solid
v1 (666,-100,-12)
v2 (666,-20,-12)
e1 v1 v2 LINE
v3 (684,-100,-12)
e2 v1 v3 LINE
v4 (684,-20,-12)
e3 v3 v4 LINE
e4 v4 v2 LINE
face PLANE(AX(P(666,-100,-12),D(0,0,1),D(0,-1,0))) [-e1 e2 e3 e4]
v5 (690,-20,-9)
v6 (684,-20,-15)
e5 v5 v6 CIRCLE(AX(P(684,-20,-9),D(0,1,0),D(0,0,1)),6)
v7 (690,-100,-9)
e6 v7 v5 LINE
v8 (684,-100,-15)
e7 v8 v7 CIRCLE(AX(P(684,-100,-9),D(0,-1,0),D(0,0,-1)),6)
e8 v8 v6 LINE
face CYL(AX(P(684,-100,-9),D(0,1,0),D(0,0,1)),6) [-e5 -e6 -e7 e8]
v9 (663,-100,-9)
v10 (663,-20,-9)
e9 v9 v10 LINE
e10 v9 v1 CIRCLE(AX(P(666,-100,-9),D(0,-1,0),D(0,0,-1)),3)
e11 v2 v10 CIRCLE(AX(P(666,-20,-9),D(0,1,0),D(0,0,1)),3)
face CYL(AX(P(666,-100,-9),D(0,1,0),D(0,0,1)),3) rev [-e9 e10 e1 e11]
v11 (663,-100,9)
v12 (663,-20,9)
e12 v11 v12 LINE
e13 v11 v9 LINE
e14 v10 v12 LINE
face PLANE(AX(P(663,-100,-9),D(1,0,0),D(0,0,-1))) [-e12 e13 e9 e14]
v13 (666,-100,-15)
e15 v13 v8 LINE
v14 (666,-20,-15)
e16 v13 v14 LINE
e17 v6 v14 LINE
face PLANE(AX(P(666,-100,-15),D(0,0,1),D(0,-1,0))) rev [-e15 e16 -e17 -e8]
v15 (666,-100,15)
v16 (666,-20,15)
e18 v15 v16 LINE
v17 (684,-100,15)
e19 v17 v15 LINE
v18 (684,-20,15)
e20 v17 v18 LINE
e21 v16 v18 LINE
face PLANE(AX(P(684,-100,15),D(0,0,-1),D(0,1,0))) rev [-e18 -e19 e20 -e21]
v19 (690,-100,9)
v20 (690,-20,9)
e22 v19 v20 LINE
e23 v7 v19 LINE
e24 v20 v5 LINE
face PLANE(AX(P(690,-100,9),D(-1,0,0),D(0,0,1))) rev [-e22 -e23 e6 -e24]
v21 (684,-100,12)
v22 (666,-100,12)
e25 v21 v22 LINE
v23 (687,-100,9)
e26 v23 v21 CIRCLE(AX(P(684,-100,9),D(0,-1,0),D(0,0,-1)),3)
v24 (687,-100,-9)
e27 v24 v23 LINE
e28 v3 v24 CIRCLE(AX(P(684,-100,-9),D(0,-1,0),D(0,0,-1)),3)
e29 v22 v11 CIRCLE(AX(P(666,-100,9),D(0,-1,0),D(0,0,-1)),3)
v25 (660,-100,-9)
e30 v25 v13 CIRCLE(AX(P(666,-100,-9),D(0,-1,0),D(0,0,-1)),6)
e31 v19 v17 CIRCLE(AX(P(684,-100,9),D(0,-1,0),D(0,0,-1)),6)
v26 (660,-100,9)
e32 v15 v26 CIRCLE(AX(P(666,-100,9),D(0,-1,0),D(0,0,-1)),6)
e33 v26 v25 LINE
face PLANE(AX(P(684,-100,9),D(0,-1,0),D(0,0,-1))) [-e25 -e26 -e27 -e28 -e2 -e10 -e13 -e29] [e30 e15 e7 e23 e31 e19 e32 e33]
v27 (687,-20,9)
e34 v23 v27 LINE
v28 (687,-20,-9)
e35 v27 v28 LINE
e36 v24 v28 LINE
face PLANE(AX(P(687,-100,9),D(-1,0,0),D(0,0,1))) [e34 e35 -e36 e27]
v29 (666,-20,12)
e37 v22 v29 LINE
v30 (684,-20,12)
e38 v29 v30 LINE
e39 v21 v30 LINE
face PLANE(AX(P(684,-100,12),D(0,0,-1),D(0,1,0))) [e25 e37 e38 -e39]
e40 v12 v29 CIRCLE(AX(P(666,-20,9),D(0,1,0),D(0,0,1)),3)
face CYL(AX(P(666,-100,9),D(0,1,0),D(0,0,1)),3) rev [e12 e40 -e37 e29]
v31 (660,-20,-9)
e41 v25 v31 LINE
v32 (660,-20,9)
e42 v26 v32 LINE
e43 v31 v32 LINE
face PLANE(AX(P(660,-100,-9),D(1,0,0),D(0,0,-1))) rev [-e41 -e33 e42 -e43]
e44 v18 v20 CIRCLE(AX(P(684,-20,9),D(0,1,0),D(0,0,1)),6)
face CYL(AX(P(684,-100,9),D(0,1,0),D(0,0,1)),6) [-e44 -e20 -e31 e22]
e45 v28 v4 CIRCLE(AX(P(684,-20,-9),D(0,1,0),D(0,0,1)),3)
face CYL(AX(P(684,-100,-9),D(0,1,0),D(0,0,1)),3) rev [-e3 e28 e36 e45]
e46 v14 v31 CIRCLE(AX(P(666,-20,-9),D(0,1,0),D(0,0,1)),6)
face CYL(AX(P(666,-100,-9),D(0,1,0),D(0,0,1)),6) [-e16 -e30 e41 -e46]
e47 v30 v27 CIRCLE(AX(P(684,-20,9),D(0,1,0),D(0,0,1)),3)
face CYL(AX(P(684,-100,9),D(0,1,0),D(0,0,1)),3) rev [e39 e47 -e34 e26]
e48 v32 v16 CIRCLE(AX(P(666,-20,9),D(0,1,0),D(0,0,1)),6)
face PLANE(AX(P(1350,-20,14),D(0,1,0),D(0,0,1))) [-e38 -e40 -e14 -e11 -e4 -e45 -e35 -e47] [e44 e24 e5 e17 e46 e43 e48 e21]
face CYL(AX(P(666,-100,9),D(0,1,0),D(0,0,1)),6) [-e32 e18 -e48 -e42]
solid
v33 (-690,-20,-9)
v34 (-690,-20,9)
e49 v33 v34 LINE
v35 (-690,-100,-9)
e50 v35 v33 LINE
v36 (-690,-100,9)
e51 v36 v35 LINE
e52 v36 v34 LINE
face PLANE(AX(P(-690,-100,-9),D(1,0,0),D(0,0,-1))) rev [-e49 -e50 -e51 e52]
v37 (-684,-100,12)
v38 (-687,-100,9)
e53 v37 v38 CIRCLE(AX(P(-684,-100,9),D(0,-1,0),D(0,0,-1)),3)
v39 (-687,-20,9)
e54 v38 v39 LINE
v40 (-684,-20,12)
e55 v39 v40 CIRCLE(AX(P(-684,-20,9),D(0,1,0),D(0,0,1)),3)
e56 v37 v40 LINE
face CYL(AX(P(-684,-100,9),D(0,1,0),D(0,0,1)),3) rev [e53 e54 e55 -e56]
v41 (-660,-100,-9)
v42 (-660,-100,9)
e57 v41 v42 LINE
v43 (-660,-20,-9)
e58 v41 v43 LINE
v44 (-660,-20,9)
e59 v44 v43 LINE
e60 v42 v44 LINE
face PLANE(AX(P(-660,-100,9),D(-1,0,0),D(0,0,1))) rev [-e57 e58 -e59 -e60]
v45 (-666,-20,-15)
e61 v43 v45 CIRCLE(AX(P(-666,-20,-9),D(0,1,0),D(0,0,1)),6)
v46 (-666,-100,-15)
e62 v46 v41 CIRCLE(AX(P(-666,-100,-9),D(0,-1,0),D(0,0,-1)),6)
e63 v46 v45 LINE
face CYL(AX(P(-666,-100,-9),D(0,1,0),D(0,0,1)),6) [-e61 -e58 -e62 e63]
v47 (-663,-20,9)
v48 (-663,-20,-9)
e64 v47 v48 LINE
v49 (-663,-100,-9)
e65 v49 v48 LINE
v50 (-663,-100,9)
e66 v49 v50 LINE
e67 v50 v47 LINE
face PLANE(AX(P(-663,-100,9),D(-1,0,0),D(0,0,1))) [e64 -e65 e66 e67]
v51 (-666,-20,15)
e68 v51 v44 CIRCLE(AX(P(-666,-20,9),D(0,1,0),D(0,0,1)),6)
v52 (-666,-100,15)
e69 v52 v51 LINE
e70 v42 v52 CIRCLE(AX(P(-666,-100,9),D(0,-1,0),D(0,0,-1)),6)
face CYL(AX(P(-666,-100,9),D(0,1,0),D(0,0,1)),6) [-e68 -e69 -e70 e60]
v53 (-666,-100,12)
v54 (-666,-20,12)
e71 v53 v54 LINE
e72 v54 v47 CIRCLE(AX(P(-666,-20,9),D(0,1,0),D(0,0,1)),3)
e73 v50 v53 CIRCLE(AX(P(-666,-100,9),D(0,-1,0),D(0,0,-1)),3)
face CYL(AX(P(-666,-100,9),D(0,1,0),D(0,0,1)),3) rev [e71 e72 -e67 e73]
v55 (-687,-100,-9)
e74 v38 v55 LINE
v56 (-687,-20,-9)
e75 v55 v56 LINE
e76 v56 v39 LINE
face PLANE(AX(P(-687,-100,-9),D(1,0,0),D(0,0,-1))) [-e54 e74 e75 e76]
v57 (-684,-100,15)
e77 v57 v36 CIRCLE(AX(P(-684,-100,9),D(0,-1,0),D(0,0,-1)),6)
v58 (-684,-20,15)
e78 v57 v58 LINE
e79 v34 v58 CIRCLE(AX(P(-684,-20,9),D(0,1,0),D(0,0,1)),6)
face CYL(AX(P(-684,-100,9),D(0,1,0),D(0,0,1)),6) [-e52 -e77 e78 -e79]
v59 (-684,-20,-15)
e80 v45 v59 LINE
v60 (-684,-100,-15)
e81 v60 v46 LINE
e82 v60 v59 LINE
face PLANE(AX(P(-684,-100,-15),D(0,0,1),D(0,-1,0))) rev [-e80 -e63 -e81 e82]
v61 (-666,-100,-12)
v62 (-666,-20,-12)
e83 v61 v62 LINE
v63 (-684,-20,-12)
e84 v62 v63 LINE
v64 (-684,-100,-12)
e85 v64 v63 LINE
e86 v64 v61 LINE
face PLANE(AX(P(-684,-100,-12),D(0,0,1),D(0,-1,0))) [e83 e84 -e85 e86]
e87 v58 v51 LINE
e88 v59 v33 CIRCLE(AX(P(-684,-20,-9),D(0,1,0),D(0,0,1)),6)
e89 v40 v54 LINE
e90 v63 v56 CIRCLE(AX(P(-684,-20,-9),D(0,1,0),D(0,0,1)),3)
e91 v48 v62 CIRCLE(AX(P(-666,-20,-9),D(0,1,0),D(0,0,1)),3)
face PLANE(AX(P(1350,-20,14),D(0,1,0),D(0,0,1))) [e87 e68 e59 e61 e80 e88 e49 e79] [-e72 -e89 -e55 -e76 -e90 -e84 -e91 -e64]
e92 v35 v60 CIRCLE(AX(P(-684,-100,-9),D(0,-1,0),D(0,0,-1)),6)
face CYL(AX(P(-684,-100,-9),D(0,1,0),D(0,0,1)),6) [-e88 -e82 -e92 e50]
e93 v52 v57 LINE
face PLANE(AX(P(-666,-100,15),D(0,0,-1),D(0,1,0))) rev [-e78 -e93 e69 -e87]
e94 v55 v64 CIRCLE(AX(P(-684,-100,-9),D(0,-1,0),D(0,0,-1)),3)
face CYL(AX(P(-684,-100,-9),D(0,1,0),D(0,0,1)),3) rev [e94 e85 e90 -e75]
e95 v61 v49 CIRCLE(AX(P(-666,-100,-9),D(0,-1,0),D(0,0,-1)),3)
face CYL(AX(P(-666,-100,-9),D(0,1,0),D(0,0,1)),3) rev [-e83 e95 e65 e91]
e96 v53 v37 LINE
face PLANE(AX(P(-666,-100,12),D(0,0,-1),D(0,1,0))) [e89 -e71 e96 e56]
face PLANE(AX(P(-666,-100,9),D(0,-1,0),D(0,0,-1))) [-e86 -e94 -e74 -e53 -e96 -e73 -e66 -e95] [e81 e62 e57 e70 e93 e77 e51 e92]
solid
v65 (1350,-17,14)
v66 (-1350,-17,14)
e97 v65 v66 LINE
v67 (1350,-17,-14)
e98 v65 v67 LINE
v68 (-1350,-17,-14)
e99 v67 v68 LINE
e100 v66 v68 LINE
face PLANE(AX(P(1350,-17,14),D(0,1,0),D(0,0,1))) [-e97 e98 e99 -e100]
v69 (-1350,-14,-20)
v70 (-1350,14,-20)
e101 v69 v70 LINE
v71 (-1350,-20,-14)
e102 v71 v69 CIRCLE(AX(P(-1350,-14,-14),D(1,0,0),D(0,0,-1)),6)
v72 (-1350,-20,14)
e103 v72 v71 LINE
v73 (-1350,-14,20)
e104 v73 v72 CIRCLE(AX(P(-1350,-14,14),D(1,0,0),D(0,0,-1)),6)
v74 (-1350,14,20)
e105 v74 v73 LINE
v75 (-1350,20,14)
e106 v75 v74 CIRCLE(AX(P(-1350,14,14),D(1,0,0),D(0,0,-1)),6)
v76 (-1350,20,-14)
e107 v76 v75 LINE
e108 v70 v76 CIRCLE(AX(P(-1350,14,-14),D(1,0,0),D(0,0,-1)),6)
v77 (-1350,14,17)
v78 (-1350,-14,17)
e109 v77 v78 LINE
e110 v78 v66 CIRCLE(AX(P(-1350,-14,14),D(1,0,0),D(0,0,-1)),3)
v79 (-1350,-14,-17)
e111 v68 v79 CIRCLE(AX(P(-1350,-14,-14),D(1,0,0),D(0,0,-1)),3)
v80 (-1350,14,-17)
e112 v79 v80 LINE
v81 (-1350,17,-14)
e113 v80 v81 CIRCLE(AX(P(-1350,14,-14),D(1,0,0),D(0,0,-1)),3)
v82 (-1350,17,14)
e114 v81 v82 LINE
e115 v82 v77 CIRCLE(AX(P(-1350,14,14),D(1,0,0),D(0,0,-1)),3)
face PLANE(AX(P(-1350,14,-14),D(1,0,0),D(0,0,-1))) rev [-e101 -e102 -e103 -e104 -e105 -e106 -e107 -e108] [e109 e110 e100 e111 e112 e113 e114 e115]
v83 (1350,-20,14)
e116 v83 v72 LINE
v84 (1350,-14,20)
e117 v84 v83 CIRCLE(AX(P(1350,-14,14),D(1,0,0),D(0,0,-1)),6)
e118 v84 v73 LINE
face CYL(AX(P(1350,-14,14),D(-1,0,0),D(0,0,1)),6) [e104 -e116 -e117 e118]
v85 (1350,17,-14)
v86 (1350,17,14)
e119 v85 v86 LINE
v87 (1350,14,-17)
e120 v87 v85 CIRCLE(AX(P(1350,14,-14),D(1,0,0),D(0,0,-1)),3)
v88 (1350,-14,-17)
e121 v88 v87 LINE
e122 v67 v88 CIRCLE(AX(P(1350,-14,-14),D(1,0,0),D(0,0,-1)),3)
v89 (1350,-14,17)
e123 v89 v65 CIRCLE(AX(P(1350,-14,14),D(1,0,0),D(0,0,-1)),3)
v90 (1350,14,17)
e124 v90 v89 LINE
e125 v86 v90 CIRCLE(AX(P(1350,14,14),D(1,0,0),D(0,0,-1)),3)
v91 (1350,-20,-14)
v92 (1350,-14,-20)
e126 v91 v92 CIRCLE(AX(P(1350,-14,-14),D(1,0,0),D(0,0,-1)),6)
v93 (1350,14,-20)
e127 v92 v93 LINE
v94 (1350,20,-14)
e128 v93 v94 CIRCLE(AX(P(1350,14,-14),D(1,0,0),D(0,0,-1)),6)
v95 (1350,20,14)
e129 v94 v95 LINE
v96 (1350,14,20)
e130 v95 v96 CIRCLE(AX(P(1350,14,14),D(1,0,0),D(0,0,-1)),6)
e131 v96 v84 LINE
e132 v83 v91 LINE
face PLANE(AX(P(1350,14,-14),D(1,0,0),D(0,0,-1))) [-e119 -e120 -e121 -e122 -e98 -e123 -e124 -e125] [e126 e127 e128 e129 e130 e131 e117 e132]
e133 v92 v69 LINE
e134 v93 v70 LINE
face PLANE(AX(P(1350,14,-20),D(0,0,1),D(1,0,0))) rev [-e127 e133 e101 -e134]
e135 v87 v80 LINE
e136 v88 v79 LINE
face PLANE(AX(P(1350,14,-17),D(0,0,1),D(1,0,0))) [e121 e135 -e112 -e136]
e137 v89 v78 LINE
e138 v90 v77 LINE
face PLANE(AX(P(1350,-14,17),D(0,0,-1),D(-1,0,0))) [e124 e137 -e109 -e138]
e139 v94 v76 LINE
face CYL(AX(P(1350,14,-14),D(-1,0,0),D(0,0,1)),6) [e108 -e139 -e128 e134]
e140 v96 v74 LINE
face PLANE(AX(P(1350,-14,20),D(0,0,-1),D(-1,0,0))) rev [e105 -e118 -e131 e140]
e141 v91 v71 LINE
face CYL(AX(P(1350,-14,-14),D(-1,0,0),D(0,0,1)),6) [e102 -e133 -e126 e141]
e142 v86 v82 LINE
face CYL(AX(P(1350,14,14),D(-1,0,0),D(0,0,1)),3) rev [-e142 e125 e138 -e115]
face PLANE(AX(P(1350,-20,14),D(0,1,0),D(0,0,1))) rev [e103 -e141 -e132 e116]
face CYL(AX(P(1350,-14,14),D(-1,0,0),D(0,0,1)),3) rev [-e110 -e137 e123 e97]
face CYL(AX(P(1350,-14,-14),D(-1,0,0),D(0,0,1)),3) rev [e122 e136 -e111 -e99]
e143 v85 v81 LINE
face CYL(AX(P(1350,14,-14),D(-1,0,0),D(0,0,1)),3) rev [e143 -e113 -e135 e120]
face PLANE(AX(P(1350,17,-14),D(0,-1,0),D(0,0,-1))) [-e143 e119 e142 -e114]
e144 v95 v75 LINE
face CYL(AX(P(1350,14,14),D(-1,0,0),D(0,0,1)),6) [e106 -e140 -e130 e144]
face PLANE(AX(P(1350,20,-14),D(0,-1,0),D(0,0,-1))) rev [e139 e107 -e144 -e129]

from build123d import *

# Parameters (mm, degrees)
GB_T6728_2002_40_X_40_X_3_1_DEPTH   = 2700
GB_T6728_2002_30_X_30_X_3_1_DEPTH   = 100
GB_T6728_2002_30_X_30_X_3_1_2_DEPTH = 100


with BuildPart() as part:
    # Sketch1 → 冷弯空心方管gb∕t6728-2002 40 X 40 X 3(1) (new body)
    with BuildSketch(Plane(origin=(-1350, 0, 0), x_dir=(0, 0, -1), z_dir=(1, 0, 0))):
        with BuildLine():
            Line((-14, -20), (14, -20))
            ThreePointArc((14, -20), (18.242640687, -18.242640687), (20, -14))
            Line((20, -14), (20, 14))
            ThreePointArc((20, 14), (18.242640687, 18.242640687), (14, 20))
            Line((14, 20), (-14, 20))
            ThreePointArc((-14, 20), (-18.242640687, 18.242640687), (-20, 14))
            Line((-20, 14), (-20, -14))
            ThreePointArc((-20, -14), (-18.242640687, -18.242640687), (-14, -20))
        make_face()
        with BuildLine():
            Line((-14, -17), (14, -17))
            ThreePointArc((14, -17), (16.121320344, -16.121320344), (17, -14))
            Line((17, -14), (17, 14))
            ThreePointArc((17, 14), (16.121320344, 16.121320344), (14, 17))
            Line((14, 17), (-14, 17))
            ThreePointArc((-14, 17), (-16.121320344, 16.121320344), (-17, 14))
            Line((-17, 14), (-17, -14))
            ThreePointArc((-17, -14), (-16.121320344, -16.121320344), (-14, -17))
        make_face(mode=Mode.SUBTRACT)
    extrude(amount=GB_T6728_2002_40_X_40_X_3_1_DEPTH)


with BuildPart() as body_2:
    # Sketch11 → 冷弯空心方管gb∕t6728-2002 30 X 30 X 3(1) (new body)
    with BuildSketch(Plane(origin=(-675, 0, 0), x_dir=(1, 0, 0), z_dir=(0, -1, 0))):
        with BuildLine():
            Line((-9, -15), (9, -15))
            ThreePointArc((9, -15), (13.242640687, -13.242640687), (15, -9))
            Line((15, -9), (15, 9))
            ThreePointArc((15, 9), (13.242640687, 13.242640687), (9, 15))
            Line((9, 15), (-9, 15))
            ThreePointArc((-9, 15), (-13.242640687, 13.242640687), (-15, 9))
            Line((-15, 9), (-15, -9))
            ThreePointArc((-15, -9), (-13.242640687, -13.242640687), (-9, -15))
        make_face()
        with BuildLine():
            Line((-9, -12), (9, -12))
            ThreePointArc((9, -12), (11.121320344, -11.121320344), (12, -9))
            Line((12, -9), (12, 9))
            ThreePointArc((12, 9), (11.121320344, 11.121320344), (9, 12))
            Line((9, 12), (-9, 12))
            ThreePointArc((-9, 12), (-11.121320344, 11.121320344), (-12, 9))
            Line((-12, 9), (-12, -9))
            ThreePointArc((-12, -9), (-11.121320344, -11.121320344), (-9, -12))
        make_face(mode=Mode.SUBTRACT)
    extrude(amount=GB_T6728_2002_30_X_30_X_3_1_DEPTH)

    # Weld Trim 1
    split(bisect_by=Plane.XZ.offset(20), keep=Keep.TOP)


with BuildPart() as body_3:
    # Sketch11 on segment 2 (carried to segment 2) → gb_t6728-2002 30 X 30 X 3_1 2 (new body)
    with BuildSketch(Plane(origin=(675, 0, 0), x_dir=(1, 0, 0), z_dir=(0, -1, 0))):
        with BuildLine():
            Line((-9, -15), (9, -15))
            ThreePointArc((9, -15), (13.242640687, -13.242640687), (15, -9))
            Line((15, -9), (15, 9))
            ThreePointArc((15, 9), (13.242640687, 13.242640687), (9, 15))
            Line((9, 15), (-9, 15))
            ThreePointArc((-9, 15), (-13.242640687, 13.242640687), (-15, 9))
            Line((-15, 9), (-15, -9))
            ThreePointArc((-15, -9), (-13.242640687, -13.242640687), (-9, -15))
        make_face()
        with BuildLine():
            Line((-9, -12), (9, -12))
            ThreePointArc((9, -12), (11.121320344, -11.121320344), (12, -9))
            Line((12, -9), (12, 9))
            ThreePointArc((12, 9), (11.121320344, 11.121320344), (9, 12))
            Line((9, 12), (-9, 12))
            ThreePointArc((-9, 12), (-11.121320344, 11.121320344), (-12, 9))
            Line((-12, 9), (-12, -9))
            ThreePointArc((-12, -9), (-11.121320344, -11.121320344), (-9, -12))
        make_face(mode=Mode.SUBTRACT)
    extrude(amount=GB_T6728_2002_30_X_30_X_3_1_2_DEPTH)

    # Weld Trim 1
    split(bisect_by=Plane.XZ.offset(20), keep=Keep.TOP)


solid = Compound([part.part, body_2.part, body_3.part])
